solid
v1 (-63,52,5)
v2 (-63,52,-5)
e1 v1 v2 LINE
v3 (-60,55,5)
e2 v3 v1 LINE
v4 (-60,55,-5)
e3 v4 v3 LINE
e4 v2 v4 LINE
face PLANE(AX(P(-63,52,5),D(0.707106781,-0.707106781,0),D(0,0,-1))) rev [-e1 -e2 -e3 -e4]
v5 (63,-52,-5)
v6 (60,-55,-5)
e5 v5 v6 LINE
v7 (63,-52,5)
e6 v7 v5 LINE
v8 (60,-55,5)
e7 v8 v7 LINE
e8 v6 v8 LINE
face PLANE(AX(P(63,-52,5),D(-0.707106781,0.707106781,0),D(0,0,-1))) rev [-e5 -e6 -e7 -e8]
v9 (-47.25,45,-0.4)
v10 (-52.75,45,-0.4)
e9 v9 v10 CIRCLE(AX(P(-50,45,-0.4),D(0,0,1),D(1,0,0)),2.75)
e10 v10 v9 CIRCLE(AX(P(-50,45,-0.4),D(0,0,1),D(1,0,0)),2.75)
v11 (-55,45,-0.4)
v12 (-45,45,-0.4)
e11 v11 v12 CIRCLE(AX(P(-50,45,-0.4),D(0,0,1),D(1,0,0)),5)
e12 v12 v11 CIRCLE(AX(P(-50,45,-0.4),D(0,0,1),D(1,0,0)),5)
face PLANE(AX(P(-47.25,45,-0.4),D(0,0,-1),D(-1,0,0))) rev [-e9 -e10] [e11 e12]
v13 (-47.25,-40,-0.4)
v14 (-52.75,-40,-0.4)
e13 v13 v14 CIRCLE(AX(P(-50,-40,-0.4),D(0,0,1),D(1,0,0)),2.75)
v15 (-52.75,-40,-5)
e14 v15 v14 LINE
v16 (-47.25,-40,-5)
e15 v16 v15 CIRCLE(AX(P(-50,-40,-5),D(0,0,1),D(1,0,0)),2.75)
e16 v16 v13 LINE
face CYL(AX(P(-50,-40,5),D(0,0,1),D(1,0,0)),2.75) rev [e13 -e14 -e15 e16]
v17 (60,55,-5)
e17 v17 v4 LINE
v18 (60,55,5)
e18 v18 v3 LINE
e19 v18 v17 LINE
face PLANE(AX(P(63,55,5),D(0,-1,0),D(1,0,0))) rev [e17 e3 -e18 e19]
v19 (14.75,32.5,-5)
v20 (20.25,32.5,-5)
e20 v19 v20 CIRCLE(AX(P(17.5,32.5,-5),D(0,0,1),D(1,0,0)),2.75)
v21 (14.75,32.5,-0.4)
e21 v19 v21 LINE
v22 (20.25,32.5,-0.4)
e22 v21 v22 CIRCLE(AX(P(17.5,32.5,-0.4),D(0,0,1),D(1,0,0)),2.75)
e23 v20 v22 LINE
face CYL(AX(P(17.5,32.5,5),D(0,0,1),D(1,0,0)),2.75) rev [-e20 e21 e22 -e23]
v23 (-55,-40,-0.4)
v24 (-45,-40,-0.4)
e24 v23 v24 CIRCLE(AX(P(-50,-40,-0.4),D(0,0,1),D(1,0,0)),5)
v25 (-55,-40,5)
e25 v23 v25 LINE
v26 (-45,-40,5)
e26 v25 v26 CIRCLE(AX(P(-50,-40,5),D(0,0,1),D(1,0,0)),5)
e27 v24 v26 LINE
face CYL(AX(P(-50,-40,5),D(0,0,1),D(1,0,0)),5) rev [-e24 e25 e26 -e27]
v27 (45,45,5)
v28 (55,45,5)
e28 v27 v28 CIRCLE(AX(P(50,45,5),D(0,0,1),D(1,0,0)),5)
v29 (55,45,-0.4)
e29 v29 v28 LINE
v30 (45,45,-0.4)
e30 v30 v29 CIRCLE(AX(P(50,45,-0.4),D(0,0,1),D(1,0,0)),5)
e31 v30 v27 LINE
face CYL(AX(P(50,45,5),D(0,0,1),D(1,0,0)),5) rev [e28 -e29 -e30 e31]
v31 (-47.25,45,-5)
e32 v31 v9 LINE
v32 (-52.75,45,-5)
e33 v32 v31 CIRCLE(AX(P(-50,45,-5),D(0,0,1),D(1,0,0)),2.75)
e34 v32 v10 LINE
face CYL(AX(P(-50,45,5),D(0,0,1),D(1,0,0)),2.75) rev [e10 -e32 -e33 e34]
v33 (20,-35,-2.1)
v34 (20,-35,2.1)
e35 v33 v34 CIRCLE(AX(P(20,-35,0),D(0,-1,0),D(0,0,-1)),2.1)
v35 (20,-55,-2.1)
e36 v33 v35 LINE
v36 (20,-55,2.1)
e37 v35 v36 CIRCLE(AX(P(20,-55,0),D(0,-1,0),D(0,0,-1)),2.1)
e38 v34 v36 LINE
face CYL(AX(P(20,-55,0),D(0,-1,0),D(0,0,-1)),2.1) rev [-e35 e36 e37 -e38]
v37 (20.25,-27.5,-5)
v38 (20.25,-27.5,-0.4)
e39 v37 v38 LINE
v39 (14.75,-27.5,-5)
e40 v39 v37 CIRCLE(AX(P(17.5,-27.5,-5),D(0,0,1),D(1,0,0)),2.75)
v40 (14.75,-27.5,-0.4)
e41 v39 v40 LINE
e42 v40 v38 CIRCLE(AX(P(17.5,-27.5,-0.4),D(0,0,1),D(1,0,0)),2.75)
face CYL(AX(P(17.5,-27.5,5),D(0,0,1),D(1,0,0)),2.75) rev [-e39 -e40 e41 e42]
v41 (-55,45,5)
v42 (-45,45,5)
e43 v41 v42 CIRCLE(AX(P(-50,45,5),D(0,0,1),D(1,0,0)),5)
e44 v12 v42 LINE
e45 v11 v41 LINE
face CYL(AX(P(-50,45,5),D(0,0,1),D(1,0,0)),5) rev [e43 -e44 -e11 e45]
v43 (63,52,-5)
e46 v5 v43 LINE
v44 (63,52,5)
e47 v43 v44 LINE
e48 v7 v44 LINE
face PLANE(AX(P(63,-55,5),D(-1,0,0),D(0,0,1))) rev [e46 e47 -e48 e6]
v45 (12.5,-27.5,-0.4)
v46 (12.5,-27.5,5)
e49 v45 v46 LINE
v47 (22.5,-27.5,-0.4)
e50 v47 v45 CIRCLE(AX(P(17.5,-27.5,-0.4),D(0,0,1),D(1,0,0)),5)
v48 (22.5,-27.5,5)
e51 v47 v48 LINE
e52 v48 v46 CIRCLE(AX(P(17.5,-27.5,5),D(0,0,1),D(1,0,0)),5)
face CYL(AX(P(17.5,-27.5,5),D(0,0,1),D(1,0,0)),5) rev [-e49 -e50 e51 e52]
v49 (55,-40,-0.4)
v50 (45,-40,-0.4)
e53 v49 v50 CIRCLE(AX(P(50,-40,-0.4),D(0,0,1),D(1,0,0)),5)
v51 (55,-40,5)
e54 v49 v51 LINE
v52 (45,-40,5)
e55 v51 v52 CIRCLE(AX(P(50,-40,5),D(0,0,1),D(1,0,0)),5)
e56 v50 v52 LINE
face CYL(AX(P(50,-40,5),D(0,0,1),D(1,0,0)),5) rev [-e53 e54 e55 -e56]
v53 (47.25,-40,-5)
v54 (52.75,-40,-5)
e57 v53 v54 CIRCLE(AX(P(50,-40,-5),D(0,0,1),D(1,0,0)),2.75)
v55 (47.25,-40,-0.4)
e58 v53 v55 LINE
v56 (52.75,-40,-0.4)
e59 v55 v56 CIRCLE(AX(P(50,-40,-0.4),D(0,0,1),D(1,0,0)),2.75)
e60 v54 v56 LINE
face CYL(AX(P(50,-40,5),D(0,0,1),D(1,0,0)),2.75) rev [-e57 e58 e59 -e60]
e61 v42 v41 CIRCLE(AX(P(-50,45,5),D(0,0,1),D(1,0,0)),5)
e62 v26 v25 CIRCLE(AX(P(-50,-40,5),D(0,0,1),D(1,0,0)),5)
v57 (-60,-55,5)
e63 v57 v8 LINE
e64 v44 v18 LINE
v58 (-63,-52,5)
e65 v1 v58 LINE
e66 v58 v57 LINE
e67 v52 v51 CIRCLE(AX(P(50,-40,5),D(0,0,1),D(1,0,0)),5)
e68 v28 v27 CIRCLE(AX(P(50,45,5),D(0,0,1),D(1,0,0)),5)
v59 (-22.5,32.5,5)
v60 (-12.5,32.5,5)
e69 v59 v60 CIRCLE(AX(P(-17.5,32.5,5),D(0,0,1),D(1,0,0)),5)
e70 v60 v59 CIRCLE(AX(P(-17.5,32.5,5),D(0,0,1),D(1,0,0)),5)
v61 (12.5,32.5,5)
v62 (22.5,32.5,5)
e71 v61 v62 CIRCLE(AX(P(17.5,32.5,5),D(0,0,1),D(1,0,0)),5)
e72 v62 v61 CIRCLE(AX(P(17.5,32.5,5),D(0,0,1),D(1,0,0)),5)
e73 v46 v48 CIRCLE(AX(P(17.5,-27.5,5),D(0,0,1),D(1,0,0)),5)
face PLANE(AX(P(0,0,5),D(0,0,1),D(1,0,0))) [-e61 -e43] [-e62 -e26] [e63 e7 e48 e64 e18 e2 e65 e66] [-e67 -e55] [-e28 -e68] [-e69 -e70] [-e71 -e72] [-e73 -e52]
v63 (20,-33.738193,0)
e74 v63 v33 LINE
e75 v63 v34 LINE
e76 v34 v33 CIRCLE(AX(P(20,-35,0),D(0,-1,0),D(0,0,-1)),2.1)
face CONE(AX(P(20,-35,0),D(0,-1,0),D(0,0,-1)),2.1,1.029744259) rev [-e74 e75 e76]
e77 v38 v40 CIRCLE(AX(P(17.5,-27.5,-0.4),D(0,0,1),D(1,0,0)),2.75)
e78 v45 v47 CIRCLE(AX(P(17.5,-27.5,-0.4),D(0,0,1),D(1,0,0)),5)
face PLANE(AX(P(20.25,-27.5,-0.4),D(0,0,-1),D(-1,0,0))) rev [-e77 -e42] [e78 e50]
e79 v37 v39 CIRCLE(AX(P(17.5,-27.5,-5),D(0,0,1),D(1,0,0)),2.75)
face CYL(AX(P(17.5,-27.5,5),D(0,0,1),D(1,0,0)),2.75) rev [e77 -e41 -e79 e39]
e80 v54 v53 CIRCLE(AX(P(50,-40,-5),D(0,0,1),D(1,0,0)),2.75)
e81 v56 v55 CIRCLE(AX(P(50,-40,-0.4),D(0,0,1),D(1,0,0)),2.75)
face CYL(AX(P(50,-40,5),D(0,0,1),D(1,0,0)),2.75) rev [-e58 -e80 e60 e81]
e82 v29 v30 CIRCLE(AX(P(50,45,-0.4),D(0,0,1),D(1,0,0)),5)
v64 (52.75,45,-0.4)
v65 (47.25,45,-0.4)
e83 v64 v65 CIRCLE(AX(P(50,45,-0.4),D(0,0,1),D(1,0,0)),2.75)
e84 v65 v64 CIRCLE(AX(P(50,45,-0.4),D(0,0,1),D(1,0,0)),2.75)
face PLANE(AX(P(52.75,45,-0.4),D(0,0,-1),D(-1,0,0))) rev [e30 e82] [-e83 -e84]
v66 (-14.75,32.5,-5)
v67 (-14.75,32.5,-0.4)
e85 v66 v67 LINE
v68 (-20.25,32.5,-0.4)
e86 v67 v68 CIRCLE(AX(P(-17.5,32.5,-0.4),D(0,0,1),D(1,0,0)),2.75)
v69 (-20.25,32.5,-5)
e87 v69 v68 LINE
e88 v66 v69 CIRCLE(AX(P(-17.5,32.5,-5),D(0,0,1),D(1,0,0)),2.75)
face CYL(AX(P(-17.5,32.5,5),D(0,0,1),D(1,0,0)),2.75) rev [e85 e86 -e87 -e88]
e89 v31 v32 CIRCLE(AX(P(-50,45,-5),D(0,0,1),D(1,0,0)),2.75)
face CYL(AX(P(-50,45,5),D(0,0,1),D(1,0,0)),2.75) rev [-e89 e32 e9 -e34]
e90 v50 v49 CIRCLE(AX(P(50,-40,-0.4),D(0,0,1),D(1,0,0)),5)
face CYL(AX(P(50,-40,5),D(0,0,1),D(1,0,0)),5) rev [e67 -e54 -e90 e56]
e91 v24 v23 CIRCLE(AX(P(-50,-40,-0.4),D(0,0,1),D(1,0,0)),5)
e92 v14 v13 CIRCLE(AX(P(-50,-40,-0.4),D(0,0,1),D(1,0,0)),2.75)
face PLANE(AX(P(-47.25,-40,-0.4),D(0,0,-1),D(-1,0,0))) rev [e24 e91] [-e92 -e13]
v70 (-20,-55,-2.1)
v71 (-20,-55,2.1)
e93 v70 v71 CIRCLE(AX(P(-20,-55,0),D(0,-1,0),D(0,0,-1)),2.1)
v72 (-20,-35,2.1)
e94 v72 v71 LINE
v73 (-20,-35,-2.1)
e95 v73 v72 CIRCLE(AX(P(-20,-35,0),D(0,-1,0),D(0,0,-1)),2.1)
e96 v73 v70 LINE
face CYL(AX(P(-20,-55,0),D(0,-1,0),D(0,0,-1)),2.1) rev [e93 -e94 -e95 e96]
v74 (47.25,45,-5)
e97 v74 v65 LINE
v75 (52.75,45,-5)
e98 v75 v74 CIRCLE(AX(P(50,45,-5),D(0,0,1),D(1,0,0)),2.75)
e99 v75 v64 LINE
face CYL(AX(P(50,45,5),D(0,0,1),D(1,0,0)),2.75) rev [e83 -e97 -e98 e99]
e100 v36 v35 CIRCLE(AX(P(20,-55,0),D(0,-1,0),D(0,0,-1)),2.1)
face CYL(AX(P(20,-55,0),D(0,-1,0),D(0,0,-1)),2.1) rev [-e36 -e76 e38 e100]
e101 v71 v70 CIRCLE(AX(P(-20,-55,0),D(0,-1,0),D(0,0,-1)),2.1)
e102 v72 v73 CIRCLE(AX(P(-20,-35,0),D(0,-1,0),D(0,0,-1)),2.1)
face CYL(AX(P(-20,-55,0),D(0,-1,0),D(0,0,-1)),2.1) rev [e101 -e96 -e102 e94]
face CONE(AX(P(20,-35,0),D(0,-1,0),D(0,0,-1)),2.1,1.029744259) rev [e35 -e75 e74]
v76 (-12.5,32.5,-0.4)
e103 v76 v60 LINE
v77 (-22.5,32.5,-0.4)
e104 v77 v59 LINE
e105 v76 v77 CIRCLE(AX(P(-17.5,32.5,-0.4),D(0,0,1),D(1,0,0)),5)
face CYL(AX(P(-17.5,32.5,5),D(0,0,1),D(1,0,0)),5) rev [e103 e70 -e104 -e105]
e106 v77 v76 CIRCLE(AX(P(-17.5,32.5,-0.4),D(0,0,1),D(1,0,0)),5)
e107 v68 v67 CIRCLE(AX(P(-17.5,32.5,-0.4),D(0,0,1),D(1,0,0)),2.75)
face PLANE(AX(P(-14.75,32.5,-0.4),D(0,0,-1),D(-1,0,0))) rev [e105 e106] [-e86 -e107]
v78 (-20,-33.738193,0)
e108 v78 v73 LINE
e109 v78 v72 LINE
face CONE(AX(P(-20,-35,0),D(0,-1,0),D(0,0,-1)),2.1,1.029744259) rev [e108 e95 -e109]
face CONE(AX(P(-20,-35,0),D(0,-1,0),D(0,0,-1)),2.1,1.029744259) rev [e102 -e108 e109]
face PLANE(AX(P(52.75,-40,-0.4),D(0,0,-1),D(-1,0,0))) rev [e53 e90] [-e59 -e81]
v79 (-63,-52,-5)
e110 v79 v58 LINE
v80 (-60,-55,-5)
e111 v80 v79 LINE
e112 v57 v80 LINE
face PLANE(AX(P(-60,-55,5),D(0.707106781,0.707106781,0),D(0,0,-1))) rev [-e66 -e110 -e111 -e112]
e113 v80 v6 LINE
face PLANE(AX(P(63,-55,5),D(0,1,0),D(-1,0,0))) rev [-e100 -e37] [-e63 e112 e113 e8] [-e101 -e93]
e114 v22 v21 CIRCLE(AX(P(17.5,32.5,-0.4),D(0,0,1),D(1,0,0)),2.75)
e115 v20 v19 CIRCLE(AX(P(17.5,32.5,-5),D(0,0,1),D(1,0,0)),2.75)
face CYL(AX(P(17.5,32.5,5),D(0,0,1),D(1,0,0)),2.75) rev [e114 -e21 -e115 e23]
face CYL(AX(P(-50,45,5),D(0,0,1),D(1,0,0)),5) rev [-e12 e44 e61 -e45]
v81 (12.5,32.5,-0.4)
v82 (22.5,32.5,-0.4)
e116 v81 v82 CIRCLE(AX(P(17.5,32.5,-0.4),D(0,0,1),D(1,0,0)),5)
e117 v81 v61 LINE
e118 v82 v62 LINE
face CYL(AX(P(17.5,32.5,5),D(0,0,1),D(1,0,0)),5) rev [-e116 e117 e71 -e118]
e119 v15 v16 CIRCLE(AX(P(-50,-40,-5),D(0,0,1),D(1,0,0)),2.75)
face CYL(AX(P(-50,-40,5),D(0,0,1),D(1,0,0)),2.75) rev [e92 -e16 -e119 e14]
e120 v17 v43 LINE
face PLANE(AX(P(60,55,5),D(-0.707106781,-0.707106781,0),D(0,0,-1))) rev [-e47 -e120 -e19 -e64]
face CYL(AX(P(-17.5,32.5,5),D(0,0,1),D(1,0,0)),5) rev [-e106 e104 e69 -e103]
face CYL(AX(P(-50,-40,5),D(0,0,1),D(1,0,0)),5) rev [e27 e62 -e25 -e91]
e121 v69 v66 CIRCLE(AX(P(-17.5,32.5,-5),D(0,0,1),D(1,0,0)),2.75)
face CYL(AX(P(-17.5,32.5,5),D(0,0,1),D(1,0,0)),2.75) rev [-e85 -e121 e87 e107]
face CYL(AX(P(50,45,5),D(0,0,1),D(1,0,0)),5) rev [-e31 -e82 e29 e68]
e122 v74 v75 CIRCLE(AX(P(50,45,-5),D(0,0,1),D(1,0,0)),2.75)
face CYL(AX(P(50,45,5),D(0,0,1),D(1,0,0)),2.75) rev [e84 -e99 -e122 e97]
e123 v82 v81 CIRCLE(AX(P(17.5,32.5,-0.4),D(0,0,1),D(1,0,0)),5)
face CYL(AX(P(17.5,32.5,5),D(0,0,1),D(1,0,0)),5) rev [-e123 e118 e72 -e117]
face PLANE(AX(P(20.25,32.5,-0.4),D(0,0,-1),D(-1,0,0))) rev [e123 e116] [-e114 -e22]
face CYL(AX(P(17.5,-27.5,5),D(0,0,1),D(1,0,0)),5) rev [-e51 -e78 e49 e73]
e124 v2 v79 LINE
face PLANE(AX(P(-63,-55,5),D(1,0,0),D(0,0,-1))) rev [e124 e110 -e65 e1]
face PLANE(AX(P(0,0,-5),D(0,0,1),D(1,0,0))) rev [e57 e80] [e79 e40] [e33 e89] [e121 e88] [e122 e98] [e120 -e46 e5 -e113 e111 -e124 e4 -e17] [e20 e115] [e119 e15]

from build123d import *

# Parameters (mm, degrees)
SKETCH_1_W                   = 126
SKETCH_1_H                   = 110
EXTRUDE_1_DEPTH              = 5
CHAMFER_1_SIZE               = 3
HOLE_WIZARD_M5_1_D           = 5.5
HOLE_WIZARD_M5_1_CBORE_D     = 10
HOLE_WIZARD_M5_1_CBORE_DEPTH = 5.4
HOLE_WIZARD_M5_1_2_D         = 4.2
HOLE_WIZARD_M5_1_2_DEPTH     = 20
HOLE_WIZARD_M5_1_2_TIP       = 1.2618073


with BuildPart() as part:
    # 草图1 → 凸台-拉伸1 (new, symmetric)
    with BuildSketch(Plane.XY):
        Rectangle(SKETCH_1_W, SKETCH_1_H)
    extrude(amount=EXTRUDE_1_DEPTH, both=True)

    # 倒角1
    chamfer_1_edges = [part.edges().sort_by_distance(p)[0] for p in [
        (-63, 55, 0),
        (63, 55, 0),
        (63, -55, 0),
        (-63, -55, 0),
    ]]
    chamfer(chamfer_1_edges, length=CHAMFER_1_SIZE)

    # Hole Wizard M5 _1 (through all)
    with Locations(Plane.XY.offset(5)):
        with Locations((-50, 45), (-17.5, 32.5), (17.5, 32.5), (50, 45), (50, -40), (17.5, -27.5), (-50, -40)):
            CounterBoreHole(HOLE_WIZARD_M5_1_D / 2, HOLE_WIZARD_M5_1_CBORE_D / 2, HOLE_WIZARD_M5_1_CBORE_DEPTH)

    # Hole Wizard M5 _1 2
    with Locations(Plane(origin=(0, -55, 0), x_dir=(-1, 0, 0), z_dir=(0, -1, 0))):
        with Locations((20, 0), (-20, 0)):
            Hole(HOLE_WIZARD_M5_1_2_D / 2, depth=HOLE_WIZARD_M5_1_2_DEPTH)
            with Locations((0, 0, -(HOLE_WIZARD_M5_1_2_DEPTH + HOLE_WIZARD_M5_1_2_TIP / 2))):  # 118° drill point
                Cone(0, HOLE_WIZARD_M5_1_2_D / 2, HOLE_WIZARD_M5_1_2_TIP, mode=Mode.SUBTRACT)


solid = part.part
